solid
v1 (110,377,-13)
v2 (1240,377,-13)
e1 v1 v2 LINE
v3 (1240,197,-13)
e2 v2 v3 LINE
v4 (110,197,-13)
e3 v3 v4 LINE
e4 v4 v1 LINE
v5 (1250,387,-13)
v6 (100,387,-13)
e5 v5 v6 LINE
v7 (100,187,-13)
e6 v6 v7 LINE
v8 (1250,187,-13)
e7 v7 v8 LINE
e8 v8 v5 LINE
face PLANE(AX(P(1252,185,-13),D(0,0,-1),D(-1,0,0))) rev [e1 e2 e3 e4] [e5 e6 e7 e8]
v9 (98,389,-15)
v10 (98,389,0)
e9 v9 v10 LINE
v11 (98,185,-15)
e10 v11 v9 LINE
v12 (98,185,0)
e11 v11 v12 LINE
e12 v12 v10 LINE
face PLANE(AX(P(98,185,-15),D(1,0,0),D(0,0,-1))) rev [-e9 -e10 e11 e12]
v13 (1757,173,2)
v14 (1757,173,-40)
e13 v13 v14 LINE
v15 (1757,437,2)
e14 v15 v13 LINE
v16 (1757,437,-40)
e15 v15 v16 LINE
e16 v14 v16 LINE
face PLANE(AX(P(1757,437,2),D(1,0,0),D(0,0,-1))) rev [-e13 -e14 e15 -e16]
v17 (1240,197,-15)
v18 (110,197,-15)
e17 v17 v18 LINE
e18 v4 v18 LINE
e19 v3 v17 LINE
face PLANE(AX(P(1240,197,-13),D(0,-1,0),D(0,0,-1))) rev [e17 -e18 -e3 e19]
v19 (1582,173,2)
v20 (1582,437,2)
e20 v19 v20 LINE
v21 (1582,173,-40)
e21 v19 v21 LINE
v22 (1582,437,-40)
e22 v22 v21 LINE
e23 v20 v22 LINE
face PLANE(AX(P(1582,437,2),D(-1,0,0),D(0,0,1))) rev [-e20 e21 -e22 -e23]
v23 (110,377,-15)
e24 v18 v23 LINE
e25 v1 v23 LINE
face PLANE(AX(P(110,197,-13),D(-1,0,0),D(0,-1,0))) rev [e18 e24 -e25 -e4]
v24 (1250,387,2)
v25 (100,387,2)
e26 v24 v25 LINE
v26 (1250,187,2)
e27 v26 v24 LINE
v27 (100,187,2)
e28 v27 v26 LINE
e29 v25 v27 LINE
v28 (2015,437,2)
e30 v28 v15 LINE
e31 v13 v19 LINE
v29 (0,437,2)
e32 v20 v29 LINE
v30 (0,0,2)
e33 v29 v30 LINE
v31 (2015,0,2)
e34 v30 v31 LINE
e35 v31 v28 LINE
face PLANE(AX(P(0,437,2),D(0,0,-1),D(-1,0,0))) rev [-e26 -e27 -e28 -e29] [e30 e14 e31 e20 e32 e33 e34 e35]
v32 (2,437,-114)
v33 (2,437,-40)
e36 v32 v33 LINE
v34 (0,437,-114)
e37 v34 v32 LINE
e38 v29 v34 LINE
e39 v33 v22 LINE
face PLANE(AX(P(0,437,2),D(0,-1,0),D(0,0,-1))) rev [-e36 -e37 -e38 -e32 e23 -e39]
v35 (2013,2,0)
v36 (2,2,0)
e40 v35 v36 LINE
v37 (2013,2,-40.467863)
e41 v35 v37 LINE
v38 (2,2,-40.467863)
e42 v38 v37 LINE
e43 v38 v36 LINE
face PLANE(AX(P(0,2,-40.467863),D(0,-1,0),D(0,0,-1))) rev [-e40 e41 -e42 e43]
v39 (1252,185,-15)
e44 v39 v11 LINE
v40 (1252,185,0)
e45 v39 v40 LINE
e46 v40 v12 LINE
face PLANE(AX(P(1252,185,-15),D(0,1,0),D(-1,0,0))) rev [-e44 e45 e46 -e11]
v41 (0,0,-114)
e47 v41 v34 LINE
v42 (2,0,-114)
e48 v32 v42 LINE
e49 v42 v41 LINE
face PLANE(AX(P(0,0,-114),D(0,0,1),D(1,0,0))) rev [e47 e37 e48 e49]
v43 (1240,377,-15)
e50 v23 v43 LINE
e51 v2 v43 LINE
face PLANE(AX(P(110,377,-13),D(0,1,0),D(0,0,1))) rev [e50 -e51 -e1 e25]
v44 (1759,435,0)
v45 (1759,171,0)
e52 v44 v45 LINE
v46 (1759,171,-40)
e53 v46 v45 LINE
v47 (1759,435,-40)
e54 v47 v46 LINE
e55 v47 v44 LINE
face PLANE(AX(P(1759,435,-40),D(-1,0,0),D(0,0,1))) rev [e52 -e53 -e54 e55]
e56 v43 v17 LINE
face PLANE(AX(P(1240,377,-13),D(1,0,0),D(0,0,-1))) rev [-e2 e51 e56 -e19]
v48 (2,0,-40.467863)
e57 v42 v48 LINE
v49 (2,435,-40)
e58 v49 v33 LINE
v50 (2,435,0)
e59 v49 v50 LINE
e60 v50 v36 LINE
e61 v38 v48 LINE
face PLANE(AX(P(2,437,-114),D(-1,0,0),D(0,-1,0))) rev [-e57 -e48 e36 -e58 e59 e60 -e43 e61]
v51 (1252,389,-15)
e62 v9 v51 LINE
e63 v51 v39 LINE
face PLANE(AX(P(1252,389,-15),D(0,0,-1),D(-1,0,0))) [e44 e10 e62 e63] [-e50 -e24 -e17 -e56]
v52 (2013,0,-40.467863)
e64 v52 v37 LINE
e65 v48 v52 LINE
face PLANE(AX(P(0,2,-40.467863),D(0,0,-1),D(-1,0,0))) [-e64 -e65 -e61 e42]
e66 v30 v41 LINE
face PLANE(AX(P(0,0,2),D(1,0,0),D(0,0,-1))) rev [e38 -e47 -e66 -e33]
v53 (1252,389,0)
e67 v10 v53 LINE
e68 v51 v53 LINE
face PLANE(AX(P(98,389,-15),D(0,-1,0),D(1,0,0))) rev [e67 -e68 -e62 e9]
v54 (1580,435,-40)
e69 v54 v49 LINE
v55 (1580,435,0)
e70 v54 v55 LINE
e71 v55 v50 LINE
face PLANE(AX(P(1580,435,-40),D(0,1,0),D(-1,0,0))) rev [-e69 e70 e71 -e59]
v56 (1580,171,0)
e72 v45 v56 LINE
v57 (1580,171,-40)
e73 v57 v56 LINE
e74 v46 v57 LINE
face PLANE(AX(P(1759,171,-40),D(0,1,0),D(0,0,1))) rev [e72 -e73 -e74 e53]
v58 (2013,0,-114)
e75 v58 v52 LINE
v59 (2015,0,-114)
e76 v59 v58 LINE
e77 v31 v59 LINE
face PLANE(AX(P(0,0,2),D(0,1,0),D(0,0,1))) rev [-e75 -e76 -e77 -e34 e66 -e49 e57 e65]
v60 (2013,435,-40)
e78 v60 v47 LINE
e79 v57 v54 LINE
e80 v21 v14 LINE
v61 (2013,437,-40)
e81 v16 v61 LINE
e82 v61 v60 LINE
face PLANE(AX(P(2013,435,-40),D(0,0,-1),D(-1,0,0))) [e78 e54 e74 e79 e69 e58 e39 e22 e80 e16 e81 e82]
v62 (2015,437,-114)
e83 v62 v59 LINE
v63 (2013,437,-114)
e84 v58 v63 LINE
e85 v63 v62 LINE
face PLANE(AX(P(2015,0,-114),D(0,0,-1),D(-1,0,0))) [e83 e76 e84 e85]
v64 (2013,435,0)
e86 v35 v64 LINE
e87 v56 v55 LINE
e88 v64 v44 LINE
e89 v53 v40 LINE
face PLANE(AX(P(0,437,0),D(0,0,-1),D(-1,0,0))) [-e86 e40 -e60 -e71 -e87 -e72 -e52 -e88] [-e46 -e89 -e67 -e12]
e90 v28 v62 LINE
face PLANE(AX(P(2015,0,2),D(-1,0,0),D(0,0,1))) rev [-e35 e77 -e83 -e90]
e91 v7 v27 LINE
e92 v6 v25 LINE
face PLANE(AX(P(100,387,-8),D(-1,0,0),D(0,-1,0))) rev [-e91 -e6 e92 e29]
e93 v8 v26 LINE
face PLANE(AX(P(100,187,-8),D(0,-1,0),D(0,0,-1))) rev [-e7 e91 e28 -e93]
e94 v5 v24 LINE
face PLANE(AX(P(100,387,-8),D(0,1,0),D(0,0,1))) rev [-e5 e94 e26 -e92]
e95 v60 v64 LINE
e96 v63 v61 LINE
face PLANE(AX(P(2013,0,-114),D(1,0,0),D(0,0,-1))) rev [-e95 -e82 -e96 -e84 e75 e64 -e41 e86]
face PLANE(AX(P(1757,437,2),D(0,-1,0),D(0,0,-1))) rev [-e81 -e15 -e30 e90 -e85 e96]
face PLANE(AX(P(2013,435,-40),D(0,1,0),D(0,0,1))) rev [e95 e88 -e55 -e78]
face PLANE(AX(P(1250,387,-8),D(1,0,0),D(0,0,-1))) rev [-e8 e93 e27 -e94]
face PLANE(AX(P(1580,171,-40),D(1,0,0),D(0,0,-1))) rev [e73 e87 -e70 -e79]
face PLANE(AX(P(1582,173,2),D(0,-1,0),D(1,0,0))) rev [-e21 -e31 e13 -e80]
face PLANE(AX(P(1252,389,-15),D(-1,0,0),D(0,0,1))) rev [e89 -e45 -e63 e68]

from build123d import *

# Parameters (mm, degrees)
EXTRUDE_1_DEPTH     = 2
SKETCH_7_W          = 2
SKETCH_7_H          = 437
EXTRUDE_2_DEPTH     = 114
SKETCH_8_W          = 2
SKETCH_8_H          = 437
EXTRUDE_3_DEPTH     = 114
EXTRUDE_4_DEPTH     = 40
SKETCH_10_W         = 1150
SKETCH_10_H         = 200
CUT_EXTRUDE_1_DEPTH = 10
SKETCH_11_W         = 2015
SKETCH_11_H         = 42.467862918
EXTRUDE_5_DEPTH     = 2
SKETCH_12_W         = 1154
SKETCH_12_H         = 204
SKETCH_12_W_2       = 1150
SKETCH_12_H_2       = 200
EXTRUDE_6_DEPTH     = 15
SKETCH_13_W         = 1154
SKETCH_13_H         = 204
SKETCH_13_W_2       = 1130
SKETCH_13_H_2       = 180
EXTRUDE_7_DEPTH     = 2


with BuildPart() as part:
    # 草图2 → 凸台-拉伸1 (new body)
    with BuildSketch(Plane.XY):
        Polygon((1757, 437), (2015, 437), (2015, 0), (0, 0), (0, 437), (1582, 437), (1582, 173), (1757, 173), align=None)
    extrude(amount=EXTRUDE_1_DEPTH)

    # 草图7 → 凸台-拉伸2 (add)
    with BuildSketch(Plane(origin=(0, 0, 0), x_dir=(-1, 0, 0), z_dir=(0, 0, -1))):
        with Locations((-2014, 218.5)):
            Rectangle(SKETCH_7_W, SKETCH_7_H)
    extrude(amount=EXTRUDE_2_DEPTH)

    # 草图8 → 凸台-拉伸3 (add)
    with BuildSketch(Plane(origin=(0, 0, 0), x_dir=(-1, 0, 0), z_dir=(0, 0, -1))):
        with Locations((-1, 218.5)):
            Rectangle(SKETCH_8_W, SKETCH_8_H)
    extrude(amount=EXTRUDE_3_DEPTH)

    # 草图9 → 凸台-拉伸4 (add)
    with BuildSketch(Plane(origin=(0, 0, 0), x_dir=(-1, 0, 0), z_dir=(0, 0, -1))):
        Polygon((-2013, 435), (-1759, 435), (-1759, 171), (-1580, 171), (-1580, 435), (-2, 435), (-2, 437), (-1582, 437), (-1582, 173), (-1757, 173), (-1757, 437), (-2013, 437), align=None)
    extrude(amount=EXTRUDE_4_DEPTH)

    # 草图10 → 切除-拉伸1 (cut)
    with BuildSketch(Plane.XY.offset(2)):
        with Locations((675, 287)):
            Rectangle(SKETCH_10_W, SKETCH_10_H)
    extrude(amount=-CUT_EXTRUDE_1_DEPTH, mode=Mode.SUBTRACT)

    # 草图11 → 凸台-拉伸5 (add)
    with BuildSketch(Plane.XZ):
        with Locations((1007.5, -19.233931459)):
            Rectangle(SKETCH_11_W, SKETCH_11_H)
    extrude(amount=-EXTRUDE_5_DEPTH)

    # 草图12 → 凸台-拉伸6 (add)
    with BuildSketch(Plane(origin=(0, 0, 0), x_dir=(-1, 0, 0), z_dir=(0, 0, -1))):
        with Locations((-675, 287)):
            Rectangle(SKETCH_12_W, SKETCH_12_H)
        with Locations((-675, 287)):
            Rectangle(SKETCH_12_W_2, SKETCH_12_H_2, mode=Mode.SUBTRACT)
    extrude(amount=EXTRUDE_6_DEPTH)

    # 草图13 → 凸台-拉伸7 (add)
    with BuildSketch(Plane(origin=(0, 0, -15), x_dir=(-1, 0, 0), z_dir=(0, 0, -1))):
        with Locations((-675, 287)):
            Rectangle(SKETCH_13_W, SKETCH_13_H)
        with Locations((-675, 287)):
            Rectangle(SKETCH_13_W_2, SKETCH_13_H_2, mode=Mode.SUBTRACT)
    extrude(amount=-EXTRUDE_7_DEPTH)


solid = part.part
